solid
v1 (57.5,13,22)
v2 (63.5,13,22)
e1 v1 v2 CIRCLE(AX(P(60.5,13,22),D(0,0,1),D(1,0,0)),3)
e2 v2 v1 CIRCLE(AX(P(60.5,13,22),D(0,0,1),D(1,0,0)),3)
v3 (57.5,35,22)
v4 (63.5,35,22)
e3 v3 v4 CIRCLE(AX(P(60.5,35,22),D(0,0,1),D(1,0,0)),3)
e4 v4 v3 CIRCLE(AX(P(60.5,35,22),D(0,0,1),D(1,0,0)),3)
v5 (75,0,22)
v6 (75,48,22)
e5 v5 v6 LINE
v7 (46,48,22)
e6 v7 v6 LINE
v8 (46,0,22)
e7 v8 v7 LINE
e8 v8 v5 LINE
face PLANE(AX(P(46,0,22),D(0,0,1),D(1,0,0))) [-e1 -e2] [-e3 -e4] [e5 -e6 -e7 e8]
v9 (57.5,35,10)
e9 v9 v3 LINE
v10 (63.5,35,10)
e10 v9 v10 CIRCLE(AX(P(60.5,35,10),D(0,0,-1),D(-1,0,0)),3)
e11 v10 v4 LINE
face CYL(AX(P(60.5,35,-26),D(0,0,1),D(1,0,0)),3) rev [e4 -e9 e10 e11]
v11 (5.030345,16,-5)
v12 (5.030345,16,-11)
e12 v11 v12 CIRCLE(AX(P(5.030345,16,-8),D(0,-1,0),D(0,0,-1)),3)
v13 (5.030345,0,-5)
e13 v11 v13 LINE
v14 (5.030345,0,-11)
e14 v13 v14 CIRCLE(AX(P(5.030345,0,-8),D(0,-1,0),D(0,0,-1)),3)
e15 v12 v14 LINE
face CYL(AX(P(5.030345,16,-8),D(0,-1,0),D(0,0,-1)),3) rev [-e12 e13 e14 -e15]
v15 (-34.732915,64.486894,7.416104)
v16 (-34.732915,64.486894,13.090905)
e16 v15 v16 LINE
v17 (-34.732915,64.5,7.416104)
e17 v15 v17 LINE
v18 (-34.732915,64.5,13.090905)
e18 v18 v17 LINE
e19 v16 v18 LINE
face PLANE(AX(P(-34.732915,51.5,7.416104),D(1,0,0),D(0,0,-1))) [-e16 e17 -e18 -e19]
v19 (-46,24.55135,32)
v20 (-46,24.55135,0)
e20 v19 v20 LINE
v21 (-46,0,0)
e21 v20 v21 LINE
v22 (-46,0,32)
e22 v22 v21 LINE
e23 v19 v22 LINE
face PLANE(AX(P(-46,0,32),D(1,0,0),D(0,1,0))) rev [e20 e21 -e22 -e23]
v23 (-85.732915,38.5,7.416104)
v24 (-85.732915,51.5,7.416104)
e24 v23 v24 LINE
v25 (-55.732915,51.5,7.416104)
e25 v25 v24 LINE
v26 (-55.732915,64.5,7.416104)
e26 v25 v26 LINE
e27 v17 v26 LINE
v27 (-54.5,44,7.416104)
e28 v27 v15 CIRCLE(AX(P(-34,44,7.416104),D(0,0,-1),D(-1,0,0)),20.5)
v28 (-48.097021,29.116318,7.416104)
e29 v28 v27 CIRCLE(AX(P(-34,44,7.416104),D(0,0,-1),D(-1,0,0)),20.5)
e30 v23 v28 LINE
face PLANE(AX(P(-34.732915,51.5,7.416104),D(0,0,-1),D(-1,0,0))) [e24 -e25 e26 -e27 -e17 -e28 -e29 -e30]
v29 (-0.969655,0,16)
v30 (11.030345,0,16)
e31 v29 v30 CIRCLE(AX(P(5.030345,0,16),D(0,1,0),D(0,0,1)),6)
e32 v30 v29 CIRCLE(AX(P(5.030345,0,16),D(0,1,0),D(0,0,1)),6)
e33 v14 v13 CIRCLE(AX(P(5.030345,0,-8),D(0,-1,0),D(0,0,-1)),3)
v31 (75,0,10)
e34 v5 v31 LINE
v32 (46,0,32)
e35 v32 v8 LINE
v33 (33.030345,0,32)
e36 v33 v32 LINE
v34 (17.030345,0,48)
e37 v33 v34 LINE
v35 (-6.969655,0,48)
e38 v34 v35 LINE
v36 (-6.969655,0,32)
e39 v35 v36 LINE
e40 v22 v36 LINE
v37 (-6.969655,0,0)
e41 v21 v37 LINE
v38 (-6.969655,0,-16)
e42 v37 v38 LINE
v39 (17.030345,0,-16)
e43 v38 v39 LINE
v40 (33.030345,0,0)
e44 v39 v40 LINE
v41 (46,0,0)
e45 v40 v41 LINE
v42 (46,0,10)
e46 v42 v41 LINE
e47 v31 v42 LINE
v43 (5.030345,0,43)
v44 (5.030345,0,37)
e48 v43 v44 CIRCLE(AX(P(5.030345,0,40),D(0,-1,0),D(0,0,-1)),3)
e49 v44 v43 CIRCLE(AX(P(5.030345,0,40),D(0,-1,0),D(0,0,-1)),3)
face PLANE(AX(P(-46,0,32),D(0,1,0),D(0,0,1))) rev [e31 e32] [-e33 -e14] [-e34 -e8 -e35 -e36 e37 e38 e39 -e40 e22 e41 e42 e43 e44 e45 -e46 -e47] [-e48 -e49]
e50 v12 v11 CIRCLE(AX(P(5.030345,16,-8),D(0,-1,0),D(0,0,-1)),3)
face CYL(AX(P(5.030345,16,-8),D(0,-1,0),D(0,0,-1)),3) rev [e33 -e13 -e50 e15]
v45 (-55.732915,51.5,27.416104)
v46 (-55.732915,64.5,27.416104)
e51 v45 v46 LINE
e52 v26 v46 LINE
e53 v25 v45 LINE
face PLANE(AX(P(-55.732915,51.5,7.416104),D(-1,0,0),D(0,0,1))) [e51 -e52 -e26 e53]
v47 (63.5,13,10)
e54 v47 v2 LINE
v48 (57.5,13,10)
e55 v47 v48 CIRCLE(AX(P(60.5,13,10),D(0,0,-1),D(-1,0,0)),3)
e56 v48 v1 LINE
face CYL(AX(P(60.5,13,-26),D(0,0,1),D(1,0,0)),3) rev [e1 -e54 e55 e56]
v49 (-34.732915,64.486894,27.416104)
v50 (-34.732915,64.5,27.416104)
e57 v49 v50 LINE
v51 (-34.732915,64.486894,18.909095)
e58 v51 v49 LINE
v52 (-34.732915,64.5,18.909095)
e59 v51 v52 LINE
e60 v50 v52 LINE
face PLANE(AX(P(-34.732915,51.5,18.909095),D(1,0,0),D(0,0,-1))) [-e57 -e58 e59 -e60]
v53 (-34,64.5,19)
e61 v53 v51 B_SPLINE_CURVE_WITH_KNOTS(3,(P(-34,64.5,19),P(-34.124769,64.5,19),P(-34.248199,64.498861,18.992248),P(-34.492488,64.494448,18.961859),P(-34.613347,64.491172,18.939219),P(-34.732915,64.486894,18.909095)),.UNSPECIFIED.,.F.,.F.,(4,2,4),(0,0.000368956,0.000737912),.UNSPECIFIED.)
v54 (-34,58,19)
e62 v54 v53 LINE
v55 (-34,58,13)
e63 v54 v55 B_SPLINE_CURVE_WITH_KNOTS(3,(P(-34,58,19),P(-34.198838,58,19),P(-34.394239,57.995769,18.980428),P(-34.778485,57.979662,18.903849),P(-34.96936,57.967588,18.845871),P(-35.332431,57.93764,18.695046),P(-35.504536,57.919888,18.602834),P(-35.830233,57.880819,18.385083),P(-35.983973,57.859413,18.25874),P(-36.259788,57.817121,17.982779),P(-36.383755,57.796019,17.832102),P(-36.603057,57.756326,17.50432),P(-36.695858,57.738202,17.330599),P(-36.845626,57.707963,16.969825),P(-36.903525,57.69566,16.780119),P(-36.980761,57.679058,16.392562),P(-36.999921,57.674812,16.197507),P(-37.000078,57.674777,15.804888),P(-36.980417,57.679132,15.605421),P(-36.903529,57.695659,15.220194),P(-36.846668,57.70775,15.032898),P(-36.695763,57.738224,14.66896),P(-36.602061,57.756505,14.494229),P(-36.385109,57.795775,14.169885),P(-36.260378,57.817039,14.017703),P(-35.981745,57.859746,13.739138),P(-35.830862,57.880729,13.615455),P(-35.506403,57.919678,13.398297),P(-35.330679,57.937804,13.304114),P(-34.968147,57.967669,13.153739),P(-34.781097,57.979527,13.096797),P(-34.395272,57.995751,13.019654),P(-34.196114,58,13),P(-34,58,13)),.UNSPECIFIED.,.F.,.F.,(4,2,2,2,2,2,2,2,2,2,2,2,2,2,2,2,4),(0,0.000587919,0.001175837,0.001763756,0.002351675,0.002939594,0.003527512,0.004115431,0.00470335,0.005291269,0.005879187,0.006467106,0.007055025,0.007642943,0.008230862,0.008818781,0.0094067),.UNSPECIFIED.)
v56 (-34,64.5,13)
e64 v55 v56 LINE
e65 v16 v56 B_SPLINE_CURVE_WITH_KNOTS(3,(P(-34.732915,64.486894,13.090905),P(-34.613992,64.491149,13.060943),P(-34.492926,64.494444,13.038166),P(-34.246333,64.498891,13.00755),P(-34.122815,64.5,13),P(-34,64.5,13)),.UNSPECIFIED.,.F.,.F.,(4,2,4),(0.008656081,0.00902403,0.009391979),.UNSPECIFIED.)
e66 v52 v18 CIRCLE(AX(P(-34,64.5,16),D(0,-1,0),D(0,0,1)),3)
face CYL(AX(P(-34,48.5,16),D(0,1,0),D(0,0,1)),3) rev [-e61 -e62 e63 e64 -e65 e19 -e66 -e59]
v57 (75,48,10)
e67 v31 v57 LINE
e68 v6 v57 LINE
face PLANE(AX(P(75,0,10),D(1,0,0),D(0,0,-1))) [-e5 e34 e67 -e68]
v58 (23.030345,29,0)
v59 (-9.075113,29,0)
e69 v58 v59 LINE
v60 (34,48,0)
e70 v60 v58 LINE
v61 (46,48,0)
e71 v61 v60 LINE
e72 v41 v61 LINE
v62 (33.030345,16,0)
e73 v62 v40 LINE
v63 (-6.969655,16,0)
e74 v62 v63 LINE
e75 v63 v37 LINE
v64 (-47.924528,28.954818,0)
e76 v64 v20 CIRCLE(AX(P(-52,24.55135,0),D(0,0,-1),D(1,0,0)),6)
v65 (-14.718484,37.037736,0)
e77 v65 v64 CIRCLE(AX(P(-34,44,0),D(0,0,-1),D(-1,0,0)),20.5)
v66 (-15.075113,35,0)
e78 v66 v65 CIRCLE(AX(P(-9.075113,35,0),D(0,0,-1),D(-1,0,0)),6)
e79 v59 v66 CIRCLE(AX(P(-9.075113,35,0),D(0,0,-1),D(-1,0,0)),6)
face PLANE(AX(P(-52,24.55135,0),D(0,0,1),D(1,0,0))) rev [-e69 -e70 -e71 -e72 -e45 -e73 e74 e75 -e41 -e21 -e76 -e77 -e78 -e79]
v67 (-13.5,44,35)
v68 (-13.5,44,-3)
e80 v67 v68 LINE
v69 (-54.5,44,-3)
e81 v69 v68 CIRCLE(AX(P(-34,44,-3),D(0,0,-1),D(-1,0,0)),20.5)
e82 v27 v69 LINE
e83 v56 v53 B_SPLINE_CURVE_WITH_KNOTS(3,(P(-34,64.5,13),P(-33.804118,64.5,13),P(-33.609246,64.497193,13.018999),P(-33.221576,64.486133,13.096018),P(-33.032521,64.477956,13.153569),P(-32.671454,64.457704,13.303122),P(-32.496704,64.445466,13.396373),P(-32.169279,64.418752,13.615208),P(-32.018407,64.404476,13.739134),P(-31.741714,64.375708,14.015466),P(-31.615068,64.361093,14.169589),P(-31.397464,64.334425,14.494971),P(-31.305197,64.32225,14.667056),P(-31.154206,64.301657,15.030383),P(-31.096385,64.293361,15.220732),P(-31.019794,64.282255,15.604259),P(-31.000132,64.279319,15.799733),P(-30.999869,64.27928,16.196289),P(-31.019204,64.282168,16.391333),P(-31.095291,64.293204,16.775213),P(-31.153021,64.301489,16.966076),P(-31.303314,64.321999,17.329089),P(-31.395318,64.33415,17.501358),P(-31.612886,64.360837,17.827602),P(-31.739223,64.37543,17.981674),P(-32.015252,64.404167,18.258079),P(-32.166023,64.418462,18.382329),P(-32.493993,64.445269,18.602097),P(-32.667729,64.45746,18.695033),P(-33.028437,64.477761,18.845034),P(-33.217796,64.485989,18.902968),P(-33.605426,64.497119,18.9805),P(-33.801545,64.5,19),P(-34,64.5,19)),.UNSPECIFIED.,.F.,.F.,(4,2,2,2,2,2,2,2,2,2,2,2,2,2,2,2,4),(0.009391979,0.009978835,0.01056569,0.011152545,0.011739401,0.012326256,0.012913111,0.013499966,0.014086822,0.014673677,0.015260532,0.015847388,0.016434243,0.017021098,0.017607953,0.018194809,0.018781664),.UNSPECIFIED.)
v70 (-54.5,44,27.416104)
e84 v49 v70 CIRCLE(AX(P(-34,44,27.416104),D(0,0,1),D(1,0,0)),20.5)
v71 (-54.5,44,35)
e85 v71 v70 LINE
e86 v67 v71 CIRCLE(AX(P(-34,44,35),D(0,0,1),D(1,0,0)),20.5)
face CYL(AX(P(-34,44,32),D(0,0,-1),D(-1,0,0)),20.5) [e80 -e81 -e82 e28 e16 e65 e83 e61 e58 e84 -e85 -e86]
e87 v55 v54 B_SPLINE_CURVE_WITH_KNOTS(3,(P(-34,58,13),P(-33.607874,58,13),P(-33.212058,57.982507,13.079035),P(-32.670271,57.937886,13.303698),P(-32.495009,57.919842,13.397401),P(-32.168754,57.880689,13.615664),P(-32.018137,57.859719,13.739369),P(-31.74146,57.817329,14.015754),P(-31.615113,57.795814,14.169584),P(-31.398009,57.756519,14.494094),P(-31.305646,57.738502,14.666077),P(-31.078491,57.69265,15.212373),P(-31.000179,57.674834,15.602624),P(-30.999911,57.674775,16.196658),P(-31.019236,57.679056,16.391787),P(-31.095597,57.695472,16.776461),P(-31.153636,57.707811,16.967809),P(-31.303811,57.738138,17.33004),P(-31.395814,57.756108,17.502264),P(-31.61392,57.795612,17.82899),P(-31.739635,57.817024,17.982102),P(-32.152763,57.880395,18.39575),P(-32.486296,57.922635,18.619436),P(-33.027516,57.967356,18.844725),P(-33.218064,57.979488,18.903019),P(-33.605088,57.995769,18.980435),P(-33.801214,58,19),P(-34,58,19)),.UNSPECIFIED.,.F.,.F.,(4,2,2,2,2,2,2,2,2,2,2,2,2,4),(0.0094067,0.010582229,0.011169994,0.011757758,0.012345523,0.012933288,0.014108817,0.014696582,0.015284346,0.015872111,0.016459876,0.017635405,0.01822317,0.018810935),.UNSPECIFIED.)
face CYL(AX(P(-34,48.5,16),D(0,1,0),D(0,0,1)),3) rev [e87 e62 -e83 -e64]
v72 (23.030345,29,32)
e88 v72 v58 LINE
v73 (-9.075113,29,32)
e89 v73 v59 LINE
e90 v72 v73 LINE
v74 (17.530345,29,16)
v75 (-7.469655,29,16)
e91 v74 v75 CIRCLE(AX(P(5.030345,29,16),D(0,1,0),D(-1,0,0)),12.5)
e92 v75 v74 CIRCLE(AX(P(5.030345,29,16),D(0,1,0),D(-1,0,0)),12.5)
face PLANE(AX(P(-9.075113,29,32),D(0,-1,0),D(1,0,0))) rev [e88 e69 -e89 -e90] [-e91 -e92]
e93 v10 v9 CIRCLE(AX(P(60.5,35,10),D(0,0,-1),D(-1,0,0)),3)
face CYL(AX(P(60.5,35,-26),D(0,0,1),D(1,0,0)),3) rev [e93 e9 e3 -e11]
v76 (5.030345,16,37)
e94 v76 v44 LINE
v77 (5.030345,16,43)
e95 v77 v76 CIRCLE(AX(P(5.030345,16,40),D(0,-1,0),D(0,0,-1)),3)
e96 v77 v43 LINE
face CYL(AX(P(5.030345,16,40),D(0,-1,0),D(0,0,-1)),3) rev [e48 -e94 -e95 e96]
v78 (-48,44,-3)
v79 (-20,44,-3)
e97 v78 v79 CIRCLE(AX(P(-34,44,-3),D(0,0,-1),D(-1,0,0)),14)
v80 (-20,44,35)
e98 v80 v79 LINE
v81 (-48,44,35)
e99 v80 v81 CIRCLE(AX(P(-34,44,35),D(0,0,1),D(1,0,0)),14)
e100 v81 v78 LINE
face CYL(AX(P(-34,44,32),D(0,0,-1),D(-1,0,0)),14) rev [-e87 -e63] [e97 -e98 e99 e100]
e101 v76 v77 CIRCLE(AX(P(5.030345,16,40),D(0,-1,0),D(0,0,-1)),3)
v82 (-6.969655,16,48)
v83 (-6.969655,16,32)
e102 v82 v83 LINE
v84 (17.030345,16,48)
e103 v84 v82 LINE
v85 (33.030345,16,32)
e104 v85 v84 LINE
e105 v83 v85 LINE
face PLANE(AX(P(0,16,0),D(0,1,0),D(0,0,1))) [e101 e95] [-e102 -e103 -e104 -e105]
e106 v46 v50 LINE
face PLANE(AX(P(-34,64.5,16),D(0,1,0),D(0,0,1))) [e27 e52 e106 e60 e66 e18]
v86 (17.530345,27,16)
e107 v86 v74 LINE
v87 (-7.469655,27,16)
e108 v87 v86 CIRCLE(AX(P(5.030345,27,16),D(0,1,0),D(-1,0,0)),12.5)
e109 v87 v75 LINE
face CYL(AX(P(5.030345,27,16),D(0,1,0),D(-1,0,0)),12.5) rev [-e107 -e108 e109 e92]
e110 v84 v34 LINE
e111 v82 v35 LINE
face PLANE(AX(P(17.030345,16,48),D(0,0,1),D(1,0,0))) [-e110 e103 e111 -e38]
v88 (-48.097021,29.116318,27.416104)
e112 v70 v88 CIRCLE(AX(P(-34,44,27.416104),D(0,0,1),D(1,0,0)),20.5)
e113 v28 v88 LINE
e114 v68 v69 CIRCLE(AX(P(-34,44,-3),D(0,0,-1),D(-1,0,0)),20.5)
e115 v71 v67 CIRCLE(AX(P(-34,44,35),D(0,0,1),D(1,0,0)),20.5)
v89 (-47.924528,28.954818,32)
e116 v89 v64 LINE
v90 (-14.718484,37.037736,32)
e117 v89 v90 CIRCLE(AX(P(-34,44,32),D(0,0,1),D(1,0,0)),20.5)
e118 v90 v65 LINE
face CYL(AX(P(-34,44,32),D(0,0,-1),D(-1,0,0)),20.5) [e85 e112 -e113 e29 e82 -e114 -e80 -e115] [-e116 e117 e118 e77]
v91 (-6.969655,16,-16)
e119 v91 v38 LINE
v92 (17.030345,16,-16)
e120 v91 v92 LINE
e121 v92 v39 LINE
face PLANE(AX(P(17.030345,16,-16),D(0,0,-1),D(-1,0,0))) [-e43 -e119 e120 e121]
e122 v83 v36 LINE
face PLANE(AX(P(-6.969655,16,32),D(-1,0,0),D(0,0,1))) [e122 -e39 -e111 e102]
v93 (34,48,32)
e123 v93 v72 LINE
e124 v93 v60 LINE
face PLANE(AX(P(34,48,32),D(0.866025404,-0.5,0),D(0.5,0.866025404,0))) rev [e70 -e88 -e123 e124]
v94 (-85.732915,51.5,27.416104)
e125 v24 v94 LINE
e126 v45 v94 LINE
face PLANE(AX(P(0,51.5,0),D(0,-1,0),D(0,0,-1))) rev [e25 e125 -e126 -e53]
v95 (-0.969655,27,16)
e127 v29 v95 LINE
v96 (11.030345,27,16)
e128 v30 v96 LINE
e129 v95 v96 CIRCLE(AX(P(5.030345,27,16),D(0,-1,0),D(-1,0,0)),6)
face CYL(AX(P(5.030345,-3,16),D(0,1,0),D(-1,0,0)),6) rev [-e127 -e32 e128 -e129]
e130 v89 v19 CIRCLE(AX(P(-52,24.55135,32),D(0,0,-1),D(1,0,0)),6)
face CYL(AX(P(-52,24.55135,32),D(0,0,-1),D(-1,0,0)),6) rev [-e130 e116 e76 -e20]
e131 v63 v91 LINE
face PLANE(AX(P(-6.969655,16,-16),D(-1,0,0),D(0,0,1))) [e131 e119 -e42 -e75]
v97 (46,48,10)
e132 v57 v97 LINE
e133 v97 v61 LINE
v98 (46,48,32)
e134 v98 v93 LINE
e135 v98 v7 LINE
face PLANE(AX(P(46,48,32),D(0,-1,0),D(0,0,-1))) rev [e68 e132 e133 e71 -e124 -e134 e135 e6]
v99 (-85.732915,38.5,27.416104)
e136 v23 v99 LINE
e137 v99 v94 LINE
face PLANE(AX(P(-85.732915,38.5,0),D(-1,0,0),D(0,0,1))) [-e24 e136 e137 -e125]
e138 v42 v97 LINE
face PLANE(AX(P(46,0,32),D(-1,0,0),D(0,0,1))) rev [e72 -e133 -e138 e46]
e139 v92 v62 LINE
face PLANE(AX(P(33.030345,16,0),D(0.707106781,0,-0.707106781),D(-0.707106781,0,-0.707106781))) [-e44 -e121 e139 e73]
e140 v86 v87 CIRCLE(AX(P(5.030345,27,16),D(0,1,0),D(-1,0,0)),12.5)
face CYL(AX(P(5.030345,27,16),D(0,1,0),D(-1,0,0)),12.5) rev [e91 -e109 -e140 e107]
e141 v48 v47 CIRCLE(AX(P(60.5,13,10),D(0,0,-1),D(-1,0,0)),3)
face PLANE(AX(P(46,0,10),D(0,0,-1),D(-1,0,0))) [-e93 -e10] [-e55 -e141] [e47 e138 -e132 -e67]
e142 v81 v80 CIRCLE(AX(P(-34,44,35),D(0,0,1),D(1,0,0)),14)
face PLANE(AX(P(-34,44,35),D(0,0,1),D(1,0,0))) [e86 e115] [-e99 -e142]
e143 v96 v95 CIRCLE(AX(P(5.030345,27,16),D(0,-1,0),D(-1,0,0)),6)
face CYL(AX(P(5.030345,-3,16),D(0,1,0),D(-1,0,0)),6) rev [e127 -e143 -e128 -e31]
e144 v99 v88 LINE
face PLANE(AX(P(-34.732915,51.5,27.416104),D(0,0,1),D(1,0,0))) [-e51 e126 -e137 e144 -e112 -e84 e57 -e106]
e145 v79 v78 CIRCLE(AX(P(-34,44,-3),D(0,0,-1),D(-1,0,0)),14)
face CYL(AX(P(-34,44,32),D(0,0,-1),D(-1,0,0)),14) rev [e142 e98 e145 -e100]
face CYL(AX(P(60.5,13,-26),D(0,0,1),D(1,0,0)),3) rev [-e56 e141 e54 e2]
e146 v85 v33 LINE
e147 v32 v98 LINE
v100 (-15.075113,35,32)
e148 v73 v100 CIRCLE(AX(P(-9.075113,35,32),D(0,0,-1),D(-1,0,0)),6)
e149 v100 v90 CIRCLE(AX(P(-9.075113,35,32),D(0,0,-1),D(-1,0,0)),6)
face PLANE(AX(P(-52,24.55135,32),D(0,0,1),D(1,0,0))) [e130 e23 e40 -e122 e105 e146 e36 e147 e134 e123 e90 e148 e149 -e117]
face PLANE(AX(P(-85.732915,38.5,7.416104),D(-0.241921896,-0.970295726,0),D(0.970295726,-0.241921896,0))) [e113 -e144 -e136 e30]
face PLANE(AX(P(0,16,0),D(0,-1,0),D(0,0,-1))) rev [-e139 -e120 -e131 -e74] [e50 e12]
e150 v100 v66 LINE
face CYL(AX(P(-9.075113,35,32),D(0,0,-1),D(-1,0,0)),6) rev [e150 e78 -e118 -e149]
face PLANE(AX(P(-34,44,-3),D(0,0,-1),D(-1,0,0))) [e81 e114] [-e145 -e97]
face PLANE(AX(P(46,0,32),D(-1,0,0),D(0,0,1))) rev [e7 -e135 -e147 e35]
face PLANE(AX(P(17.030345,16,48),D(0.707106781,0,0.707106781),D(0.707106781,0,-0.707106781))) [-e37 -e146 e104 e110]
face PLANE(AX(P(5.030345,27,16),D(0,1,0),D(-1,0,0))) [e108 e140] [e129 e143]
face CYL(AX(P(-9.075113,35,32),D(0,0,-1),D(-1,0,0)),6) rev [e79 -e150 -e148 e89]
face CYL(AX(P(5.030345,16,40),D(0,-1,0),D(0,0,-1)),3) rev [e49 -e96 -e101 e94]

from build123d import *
from build123d.topology import SkipClean

# Parameters (mm, degrees)
PEDESTAL_PROFILE_SKETCH_R       = 14
PEDESTAL_BODY_DEPTH             = 32
VERTICAL_BORE_SKETCH_R          = 6
VERTICAL_BORE_16_DEPTH          = 32
COUNTERBORE_SKETCH_R            = 12.5
COUNTERBORE_25X2_DEPTH          = 2
SIDE_MOUNTING_BLOCK_SKETCH_W    = 29
SIDE_MOUNTING_BLOCK_SKETCH_H    = 12
SIDE_MOUNTING_BLOCK_DEPTH       = 48
BLOCK_MOUNTING_HOLES_SKETCH_R   = 3
BLOCK_MOUNTING_HOLES_2X_6_DEPTH = 48
T_SLOT_FLANGE_SKETCH_R          = 3
T_SLOT_FLANGE_DEPTH             = 16
TOP_HOLE_SKETCH_R               = 3
TOP_HOLE_6_DEPTH                = 16
UPPER_ARM_BLOCK_DEPTH           = 13
TRUNNION_START                  = -60
TRUNNION_BORE_SKETCH_A_R        = 14
TRUNNION_BORE_28_A_DEPTH        = 60
UPPER_ARM_EXTENSION_SKETCH_W    = 30
UPPER_ARM_EXTENSION_SKETCH_H    = 20
UPPER_ARM_EXTENSION_SKETCH_W_2  = 6.345868722
UPPER_ARM_EXTENSION_SKETCH_W_3  = 2.654131278
UPPER_ARM_EXTENSION_DEPTH       = 13
ANGLED_START                    = -20
ANGLED_SIDE_LUG_DEPTH           = 20
TRUNNION_BORE_SKETCH_B_R        = 14
TRUNNION_BORE_28_B_DEPTH        = 60
BORE_COLLAR_SKETCH_A_R          = 20.5
BORE_COLLAR_SKETCH_A_R_2        = 14
BORE_COLLAR_41X3_A_DEPTH        = 3
BORE_START                      = 3
BORE_COLLAR_SKETCH_B_R          = 20.5
BORE_COLLAR_SKETCH_B_R_2        = 14
BORE_COLLAR_41X3_B_DEPTH        = 3


with BuildPart() as part:
    # Pedestal Profile Sketch → Pedestal Body (new body)
    with BuildSketch(Plane.XY):
        with BuildLine():
            Line((-46, 0), (46, 0))
            Line((46, 0), (46, 48))
            Line((46, 48), (34, 48))
            Line((34, 48), (23.030344885, 29))
            Line((23.030344885, 29), (-9.075112839, 29))
            ThreePointArc((-9.075112839, 29), (-13.985632928, 31.552277208), (-14.718483517, 37.037735849))
            ThreePointArc((-14.718483517, 37.037735849), (-38.848476276, 63.918390442), (-47.924528302, 28.954817662))
            ThreePointArc((-47.924528302, 28.954817662), (-46.5021445, 26.954178183), (-46, 24.551349661))
            Line((-46, 24.551349661), (-46, 0))
        make_face()
        with Locations((-34, 44)):
            Circle(PEDESTAL_PROFILE_SKETCH_R, mode=Mode.SUBTRACT)
    extrude(amount=PEDESTAL_BODY_DEPTH)

    # Vertical Bore Sketch → Vertical Bore Ø16 (cut)
    with BuildSketch(Plane(origin=(0, 29, 0), x_dir=(1, 0, 0), z_dir=(0, 1, 0))):
        with Locations(Location((5.030344885, -16, 0), (0, 0, 180))):
            Circle(VERTICAL_BORE_SKETCH_R)
    extrude(amount=-VERTICAL_BORE_16_DEPTH, mode=Mode.SUBTRACT)

    # Counterbore Sketch → Counterbore Ø25x2 (cut)
    with BuildSketch(Plane(origin=(0, 29, 0), x_dir=(1, 0, 0), z_dir=(0, 1, 0))):
        with Locations(Location((5.030344885, -16, 0), (0, 0, 180))):
            Circle(COUNTERBORE_SKETCH_R)
    extrude(amount=-COUNTERBORE_25X2_DEPTH, mode=Mode.SUBTRACT)

    # Side Mounting Block Sketch → Side Mounting Block (add)
    with BuildSketch(Plane(origin=(0, 48, 0), x_dir=(1, 0, 0), z_dir=(0, 1, 0))):
        with Locations((60.5, -16)):
            Rectangle(SIDE_MOUNTING_BLOCK_SKETCH_W, SIDE_MOUNTING_BLOCK_SKETCH_H)
    extrude(amount=-SIDE_MOUNTING_BLOCK_DEPTH)

    # Block Mounting Holes Sketch → Block Mounting Holes 2xØ6 (cut)
    with BuildSketch(Plane.XY.offset(22)):
        with Locations((60.5, 35)):
            Circle(BLOCK_MOUNTING_HOLES_SKETCH_R)
        with Locations((60.5, 13)):
            Circle(BLOCK_MOUNTING_HOLES_SKETCH_R)
    extrude(amount=-BLOCK_MOUNTING_HOLES_2X_6_DEPTH, mode=Mode.SUBTRACT)

    # T-Slot Flange Sketch → T-Slot Flange (add)
    # profile 1 of 2: a face of its own
    with BuildSketch(Plane.XZ):
        Polygon((-6.969655115, -16), (-6.969655115, 0), (33.030344885, 0), (17.030344885, -16), align=None)
        with Locations(Location((5.030344885, -8, 0), (0, 0, 270))):
            Circle(T_SLOT_FLANGE_SKETCH_R, mode=Mode.SUBTRACT)
    # profile 2 of 2: a face of its own
    with BuildSketch(Plane.XZ):
        Polygon((17.030344885, 48), (-6.969655115, 48), (-6.969655115, 32), (33.030344885, 32), align=None)
        with Locations(Location((5.030344885, 40, 0), (0, 0, 270))):
            Circle(T_SLOT_FLANGE_SKETCH_R, mode=Mode.SUBTRACT)
    extrude(amount=-T_SLOT_FLANGE_DEPTH)

    # Top Hole Sketch → Top Hole Ø6 (cut)
    with BuildSketch(Plane(origin=(0, 64.5, 0), x_dir=(1, 0, 0), z_dir=(0, 1, 0))):
        with Locations(Location((-34, -16, 0), (0, 0, 270))):
            Circle(TOP_HOLE_SKETCH_R)
    extrude(amount=-TOP_HOLE_6_DEPTH, mode=Mode.SUBTRACT)

    # Upper Arm Block Sketch → Upper Arm Block (add)
    with BuildSketch(Plane(origin=(0, 64.5, 0), x_dir=(1, 0, 0), z_dir=(0, 1, 0))):
        with BuildLine():
            Line((-34.732915306, -7.416104235), (-55.732915306, -7.416104235))
            Line((-55.732915306, -7.416104235), (-55.732915306, -27.416104235))
            Line((-55.732915306, -27.416104235), (-34.732915306, -27.416104235))
            Line((-34.732915306, -27.416104235), (-34.732915306, -18.909095247))
            ThreePointArc((-34.732915306, -18.909095247), (-37, -16), (-34.732915306, -13.090904753))
            Line((-34.732915306, -13.090904753), (-34.732915306, -7.416104235))
        make_face()
    extrude(amount=-UPPER_ARM_BLOCK_DEPTH)

    # Trunnion Bore Sketch A → Trunnion Bore Ø28 A (cut)
    with BuildSketch(Plane.XY.offset(32).offset(TRUNNION_START)):
        with Locations((-34, 44)):
            Circle(TRUNNION_BORE_SKETCH_A_R)
    extrude(amount=TRUNNION_BORE_28_A_DEPTH, mode=Mode.SUBTRACT)

    # Upper Arm Extension Sketch → Upper Arm Extension (add)
    with BuildSketch(Plane.XZ.offset(-51.5)):
        with Locations((-70.732915306, 17.416104235)):
            Rectangle(UPPER_ARM_EXTENSION_SKETCH_W, UPPER_ARM_EXTENSION_SKETCH_H)
        with Locations((-49.905849667, 17.416104235)):
            Rectangle(UPPER_ARM_EXTENSION_SKETCH_W_2, UPPER_ARM_EXTENSION_SKETCH_H)
        with Locations((-54.405849667, 17.416104235)):
            Rectangle(UPPER_ARM_EXTENSION_SKETCH_W_3, UPPER_ARM_EXTENSION_SKETCH_H)
    extrude(amount=UPPER_ARM_EXTENSION_DEPTH)

    # Angled Side Lug Sketch → Angled Side Lug (add)
    with BuildSketch(Plane.XY.offset(27.416104235).offset(ANGLED_START)):
        with BuildLine():
            Line((-85.732915306, 38.5), (-48.097020916, 29.116317616))
            ThreePointArc((-48.097020916, 29.116317616), (-51.561087718, 33.423696385), (-53.748417658, 38.5))
            Line((-53.748417658, 38.5), (-85.732915306, 38.5))
        make_face()
    extrude(amount=ANGLED_SIDE_LUG_DEPTH)

    # Trunnion Bore Sketch B → Trunnion Bore Ø28 B (cut)
    with BuildSketch(Plane.XY.offset(32).offset(TRUNNION_START)):
        with Locations((-34, 44)):
            Circle(TRUNNION_BORE_SKETCH_B_R)
    extrude(amount=TRUNNION_BORE_28_B_DEPTH, mode=Mode.SUBTRACT)

    # Bore Collar Sketch A → Bore Collar Ø41x3 A (add)
    with BuildSketch(Plane.XY.offset(32)):
        with Locations(Location((-34, 44, 0), (0, 0, 227.215305089))):
            Circle(BORE_COLLAR_SKETCH_A_R)
        with Locations((-34, 44)):
            Circle(BORE_COLLAR_SKETCH_A_R_2, mode=Mode.SUBTRACT)
    extrude(amount=BORE_COLLAR_41X3_A_DEPTH)

    # Bore Collar Sketch B → Bore Collar Ø41x3 B (add)
    with SkipClean():  # the faces are left unmerged after this step: merging them gives an invalid solid
        with BuildSketch(Plane(origin=(0, 0, 0), x_dir=(-1, 0, 0), z_dir=(0, 0, -1)).offset(BORE_START)):
            with Locations((34, 44)):
                Circle(BORE_COLLAR_SKETCH_B_R)
            with Locations((34, 44)):
                Circle(BORE_COLLAR_SKETCH_B_R_2, mode=Mode.SUBTRACT)
        extrude(amount=-BORE_COLLAR_41X3_B_DEPTH)


solid = part.part
